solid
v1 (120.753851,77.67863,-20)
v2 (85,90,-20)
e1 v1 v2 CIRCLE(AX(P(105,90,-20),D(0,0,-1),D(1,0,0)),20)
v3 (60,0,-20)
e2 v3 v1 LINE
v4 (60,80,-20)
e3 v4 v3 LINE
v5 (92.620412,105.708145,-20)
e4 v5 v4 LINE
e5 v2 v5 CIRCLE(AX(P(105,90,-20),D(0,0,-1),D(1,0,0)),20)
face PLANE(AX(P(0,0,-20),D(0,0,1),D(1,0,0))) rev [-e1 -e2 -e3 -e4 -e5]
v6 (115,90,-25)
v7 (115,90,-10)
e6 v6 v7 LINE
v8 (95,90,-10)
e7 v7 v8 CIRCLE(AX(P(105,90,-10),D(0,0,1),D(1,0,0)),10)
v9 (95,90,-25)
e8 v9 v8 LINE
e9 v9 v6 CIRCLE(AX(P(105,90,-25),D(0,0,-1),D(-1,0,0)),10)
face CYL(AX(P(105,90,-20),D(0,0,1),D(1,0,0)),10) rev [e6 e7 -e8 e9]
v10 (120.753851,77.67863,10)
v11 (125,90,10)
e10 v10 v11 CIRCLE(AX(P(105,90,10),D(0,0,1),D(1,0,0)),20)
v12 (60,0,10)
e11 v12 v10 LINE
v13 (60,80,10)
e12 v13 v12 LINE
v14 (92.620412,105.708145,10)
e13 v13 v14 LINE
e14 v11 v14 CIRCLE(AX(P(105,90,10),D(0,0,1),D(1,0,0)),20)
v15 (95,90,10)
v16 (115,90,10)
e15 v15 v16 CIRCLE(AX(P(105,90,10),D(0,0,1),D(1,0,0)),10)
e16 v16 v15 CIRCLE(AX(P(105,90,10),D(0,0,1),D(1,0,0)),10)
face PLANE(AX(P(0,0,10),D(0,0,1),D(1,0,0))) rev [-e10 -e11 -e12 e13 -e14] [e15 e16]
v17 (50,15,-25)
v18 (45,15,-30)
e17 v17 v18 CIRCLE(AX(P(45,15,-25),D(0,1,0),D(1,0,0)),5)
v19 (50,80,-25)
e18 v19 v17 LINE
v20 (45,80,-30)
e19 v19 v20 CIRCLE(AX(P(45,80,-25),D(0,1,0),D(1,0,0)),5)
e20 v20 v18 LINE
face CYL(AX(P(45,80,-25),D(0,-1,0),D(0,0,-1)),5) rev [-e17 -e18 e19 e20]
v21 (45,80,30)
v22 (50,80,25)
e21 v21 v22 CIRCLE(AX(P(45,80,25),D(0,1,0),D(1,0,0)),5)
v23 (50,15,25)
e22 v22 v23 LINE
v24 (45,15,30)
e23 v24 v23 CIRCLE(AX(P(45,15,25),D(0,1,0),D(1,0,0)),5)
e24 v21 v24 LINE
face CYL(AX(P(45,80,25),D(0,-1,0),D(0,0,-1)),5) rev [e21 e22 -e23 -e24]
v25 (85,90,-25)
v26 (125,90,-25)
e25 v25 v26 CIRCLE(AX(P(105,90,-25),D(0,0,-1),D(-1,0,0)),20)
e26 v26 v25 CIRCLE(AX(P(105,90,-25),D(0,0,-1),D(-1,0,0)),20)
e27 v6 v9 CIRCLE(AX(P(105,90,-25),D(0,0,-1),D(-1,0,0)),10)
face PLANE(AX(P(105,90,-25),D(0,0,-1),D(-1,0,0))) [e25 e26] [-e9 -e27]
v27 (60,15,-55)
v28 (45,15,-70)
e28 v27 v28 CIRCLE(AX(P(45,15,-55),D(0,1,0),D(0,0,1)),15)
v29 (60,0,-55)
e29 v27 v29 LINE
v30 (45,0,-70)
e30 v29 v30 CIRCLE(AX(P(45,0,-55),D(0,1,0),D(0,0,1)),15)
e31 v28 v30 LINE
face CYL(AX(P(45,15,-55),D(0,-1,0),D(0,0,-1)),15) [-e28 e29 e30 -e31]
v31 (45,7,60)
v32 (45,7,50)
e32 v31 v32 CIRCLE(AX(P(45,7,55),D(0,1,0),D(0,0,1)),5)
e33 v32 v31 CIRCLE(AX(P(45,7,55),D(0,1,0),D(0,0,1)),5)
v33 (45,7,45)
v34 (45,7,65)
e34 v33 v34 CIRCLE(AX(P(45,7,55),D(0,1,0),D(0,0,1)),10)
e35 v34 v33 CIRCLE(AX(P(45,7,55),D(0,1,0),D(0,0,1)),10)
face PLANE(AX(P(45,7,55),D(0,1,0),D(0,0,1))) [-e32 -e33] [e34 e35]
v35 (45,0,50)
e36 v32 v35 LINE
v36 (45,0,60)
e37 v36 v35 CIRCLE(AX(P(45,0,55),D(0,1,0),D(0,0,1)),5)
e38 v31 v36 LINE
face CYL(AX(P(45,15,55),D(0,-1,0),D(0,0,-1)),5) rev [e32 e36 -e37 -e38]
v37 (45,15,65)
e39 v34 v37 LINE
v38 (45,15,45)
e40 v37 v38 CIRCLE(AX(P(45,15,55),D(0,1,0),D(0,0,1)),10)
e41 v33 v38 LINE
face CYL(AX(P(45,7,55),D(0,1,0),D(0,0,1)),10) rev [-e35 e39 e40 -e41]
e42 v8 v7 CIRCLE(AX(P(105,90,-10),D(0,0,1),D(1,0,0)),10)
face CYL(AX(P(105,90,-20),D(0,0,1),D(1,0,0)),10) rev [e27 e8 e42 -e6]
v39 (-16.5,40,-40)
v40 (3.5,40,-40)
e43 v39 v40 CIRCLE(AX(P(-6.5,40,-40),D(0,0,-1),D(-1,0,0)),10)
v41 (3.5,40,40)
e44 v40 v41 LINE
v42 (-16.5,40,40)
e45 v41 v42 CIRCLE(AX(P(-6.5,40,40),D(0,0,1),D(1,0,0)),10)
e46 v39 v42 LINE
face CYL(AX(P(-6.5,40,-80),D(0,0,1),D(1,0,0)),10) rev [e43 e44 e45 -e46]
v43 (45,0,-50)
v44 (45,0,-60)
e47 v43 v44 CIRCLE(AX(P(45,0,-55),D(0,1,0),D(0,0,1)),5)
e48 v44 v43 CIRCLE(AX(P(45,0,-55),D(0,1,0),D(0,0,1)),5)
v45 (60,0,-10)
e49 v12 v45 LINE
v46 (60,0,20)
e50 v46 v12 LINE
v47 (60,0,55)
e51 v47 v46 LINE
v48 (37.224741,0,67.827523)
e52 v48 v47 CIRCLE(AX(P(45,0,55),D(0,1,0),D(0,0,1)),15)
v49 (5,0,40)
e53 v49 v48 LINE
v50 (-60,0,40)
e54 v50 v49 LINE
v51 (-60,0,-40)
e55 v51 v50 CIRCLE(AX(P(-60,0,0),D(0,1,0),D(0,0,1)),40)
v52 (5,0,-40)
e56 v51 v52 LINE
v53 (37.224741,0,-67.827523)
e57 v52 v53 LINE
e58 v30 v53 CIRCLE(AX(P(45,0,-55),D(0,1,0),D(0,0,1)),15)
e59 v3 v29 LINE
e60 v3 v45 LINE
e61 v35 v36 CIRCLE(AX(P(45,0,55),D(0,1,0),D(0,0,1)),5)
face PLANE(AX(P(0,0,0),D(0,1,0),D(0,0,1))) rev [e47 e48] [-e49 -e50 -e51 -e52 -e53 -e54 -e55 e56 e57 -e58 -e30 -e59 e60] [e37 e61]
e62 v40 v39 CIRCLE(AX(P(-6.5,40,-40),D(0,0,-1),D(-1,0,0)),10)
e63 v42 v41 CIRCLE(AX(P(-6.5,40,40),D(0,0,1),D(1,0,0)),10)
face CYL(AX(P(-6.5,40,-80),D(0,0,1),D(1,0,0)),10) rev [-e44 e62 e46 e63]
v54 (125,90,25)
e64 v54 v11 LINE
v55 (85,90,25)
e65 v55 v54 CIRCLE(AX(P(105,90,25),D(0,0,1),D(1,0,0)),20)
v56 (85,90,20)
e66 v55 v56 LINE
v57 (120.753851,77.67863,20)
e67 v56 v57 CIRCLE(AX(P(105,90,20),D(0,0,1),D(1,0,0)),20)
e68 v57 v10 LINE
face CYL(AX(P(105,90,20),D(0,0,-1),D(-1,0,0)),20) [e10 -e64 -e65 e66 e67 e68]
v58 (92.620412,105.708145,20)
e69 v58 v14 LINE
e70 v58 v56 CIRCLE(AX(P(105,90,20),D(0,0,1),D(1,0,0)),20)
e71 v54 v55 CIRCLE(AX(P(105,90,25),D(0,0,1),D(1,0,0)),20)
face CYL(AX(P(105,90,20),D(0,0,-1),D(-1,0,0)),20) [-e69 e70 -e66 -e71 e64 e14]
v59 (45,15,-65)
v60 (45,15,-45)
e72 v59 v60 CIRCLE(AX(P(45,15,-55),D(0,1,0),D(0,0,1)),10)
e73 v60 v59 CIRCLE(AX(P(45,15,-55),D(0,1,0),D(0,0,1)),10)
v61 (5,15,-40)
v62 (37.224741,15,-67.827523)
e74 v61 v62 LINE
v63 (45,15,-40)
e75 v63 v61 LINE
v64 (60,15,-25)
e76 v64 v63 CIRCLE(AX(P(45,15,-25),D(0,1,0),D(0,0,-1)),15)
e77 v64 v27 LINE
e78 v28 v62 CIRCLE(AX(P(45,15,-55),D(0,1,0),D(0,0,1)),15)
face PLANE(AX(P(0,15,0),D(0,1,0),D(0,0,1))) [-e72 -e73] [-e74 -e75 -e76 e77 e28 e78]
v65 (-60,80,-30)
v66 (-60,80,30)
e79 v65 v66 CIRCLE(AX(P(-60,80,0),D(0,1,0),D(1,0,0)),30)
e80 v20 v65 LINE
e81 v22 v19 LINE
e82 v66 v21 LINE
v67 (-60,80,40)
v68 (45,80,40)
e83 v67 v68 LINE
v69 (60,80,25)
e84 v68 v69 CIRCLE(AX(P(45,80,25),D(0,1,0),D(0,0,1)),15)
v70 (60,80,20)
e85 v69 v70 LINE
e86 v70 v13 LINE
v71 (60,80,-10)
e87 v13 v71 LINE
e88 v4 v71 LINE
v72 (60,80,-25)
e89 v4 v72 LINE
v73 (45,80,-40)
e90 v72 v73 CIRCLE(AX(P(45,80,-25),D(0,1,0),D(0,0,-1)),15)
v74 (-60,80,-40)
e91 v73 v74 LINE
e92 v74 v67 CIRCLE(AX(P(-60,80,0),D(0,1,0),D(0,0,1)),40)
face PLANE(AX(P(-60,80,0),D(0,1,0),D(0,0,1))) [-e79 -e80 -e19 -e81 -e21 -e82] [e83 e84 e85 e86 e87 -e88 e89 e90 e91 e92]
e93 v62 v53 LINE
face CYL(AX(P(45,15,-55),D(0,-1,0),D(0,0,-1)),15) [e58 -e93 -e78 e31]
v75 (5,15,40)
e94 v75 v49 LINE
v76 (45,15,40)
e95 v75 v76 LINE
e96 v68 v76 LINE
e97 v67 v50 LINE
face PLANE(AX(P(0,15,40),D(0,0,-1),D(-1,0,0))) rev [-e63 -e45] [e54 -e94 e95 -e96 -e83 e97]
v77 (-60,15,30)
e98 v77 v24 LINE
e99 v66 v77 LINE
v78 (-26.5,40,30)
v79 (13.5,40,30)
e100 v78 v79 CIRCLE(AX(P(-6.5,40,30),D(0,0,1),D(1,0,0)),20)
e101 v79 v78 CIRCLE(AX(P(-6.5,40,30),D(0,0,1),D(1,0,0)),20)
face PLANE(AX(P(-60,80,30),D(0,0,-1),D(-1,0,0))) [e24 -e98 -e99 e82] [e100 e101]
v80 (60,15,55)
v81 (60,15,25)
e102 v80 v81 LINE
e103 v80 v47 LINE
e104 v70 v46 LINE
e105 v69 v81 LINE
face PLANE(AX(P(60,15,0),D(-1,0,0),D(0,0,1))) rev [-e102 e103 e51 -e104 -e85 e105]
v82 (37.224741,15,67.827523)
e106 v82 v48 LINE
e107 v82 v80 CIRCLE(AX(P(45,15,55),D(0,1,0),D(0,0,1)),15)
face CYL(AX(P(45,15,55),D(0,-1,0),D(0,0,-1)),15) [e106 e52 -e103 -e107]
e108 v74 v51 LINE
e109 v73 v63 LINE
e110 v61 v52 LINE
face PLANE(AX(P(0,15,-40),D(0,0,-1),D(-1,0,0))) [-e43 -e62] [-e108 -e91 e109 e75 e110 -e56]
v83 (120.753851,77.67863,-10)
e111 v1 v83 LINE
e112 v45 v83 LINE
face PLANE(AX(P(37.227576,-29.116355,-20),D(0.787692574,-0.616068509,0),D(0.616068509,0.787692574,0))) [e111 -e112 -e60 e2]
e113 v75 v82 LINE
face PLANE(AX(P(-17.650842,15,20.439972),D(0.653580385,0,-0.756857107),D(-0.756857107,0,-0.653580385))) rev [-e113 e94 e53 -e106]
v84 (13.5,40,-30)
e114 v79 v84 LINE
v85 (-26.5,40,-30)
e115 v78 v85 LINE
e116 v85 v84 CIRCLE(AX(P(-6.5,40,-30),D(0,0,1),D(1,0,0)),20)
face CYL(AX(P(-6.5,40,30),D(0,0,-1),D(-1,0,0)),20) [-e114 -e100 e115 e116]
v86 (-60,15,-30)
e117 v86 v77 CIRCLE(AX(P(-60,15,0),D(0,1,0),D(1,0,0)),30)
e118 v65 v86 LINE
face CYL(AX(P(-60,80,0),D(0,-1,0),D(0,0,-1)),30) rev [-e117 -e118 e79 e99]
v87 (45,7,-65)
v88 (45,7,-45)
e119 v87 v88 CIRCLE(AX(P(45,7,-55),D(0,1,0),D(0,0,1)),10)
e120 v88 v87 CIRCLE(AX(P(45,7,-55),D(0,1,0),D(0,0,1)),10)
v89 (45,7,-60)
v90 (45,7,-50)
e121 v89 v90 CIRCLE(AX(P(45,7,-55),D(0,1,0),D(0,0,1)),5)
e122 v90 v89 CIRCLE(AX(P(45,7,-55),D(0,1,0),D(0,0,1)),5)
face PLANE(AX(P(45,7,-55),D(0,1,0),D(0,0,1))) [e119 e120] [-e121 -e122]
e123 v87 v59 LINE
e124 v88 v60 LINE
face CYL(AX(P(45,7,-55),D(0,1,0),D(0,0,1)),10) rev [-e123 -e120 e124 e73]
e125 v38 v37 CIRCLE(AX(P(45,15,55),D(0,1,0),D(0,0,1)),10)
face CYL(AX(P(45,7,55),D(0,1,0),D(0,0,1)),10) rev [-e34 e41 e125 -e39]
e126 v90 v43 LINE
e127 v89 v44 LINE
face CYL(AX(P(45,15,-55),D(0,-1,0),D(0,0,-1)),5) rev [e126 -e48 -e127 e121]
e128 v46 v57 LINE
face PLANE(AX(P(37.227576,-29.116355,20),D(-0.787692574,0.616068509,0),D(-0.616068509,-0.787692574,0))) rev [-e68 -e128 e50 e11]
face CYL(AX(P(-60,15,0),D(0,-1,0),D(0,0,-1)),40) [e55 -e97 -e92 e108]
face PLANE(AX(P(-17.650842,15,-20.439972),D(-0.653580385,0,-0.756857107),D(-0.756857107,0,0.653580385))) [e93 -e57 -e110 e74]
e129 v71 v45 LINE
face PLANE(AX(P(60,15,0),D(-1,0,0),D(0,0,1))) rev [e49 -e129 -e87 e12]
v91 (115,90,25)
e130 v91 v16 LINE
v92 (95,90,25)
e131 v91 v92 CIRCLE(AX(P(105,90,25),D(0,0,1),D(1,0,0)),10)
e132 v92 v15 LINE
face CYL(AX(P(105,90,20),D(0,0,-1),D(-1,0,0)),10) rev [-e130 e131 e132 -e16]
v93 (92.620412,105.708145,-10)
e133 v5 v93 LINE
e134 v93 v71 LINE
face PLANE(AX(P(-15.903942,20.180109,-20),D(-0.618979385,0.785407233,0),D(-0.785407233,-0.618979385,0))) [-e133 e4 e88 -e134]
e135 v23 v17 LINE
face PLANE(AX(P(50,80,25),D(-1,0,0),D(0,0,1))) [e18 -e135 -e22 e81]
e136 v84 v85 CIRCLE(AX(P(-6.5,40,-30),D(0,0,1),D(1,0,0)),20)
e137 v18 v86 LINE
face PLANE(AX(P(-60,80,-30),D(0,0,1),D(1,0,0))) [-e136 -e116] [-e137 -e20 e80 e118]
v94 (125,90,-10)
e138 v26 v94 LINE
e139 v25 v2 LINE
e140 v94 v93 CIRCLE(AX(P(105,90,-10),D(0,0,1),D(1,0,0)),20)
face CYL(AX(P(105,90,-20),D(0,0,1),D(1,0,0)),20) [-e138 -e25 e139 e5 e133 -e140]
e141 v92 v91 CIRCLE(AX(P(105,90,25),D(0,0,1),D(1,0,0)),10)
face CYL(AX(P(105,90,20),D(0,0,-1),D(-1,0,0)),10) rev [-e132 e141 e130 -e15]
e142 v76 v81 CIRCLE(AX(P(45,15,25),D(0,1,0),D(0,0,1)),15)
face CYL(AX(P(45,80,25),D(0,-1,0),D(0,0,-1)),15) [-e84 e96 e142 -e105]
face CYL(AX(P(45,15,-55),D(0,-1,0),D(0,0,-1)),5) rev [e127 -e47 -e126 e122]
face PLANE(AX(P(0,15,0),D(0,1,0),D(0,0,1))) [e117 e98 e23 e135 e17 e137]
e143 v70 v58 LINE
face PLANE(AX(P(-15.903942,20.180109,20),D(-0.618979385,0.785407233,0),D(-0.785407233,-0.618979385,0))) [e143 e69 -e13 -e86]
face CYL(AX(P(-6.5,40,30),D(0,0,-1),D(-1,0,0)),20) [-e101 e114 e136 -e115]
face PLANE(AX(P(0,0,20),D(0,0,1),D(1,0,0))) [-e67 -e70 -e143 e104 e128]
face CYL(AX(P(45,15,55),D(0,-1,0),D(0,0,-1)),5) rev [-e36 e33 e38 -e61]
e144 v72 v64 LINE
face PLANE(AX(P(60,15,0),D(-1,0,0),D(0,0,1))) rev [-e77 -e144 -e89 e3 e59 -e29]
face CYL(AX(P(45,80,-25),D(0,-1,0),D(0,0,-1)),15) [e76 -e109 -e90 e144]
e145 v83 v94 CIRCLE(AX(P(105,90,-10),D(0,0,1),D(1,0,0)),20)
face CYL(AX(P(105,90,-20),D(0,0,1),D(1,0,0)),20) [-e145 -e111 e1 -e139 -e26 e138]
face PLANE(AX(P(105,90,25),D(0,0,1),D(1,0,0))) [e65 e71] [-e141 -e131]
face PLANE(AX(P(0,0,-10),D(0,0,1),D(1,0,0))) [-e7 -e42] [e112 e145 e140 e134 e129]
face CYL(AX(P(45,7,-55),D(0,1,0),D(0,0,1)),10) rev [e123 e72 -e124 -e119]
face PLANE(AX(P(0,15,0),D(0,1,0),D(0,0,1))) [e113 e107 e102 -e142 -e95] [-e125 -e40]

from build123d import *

# Parameters (mm, degrees)
BASE_PLATE_SKETCH_R       = 5
BASE_PLATE_DEPTH          = 15
HOUSING_WALL_DEPTH        = 65
EAR_RECESSES_SKETCH_R     = 10
EAR_RECESSES_2X_20_DEPTH  = 8
CROSS_BORE_SKETCH_R       = 10
CROSS_BORE_DEPTH          = 120
CROSS_START               = 60
CROSS_PIN_SKETCH_R        = 20
CROSS_PIN_SKETCH_R_2      = 10
CROSS_PIN_DEPTH           = 60
LUG_1_SKETCH_R            = 20
LUG_1_SKETCH_R_2          = 10
LUG_1_DEPTH               = 10
LUG_1_PIN_BOSS_SKETCH_R   = 20
LUG_1_PIN_BOSS_SKETCH_R_2 = 10
LUG_1_PIN_BOSS_DEPTH      = 5
LUG_START                 = -10
LUG_2_SKETCH_R            = 20
LUG_2_SKETCH_R_2          = 10
LUG_2_DEPTH               = 10
LUG_START_2               = 5
LUG_2_PIN_BOSS_SKETCH_R   = 20
LUG_2_PIN_BOSS_SKETCH_R_2 = 10
LUG_2_PIN_BOSS_DEPTH      = 5


with BuildPart() as part:
    # Base Plate Sketch → Base Plate (new body)
    # profile 1 of 3: a face of its own
    with BuildSketch(Plane(origin=(0, 0, 0), x_dir=(1, 0, 0), z_dir=(0, 1, 0))):
        with BuildLine():
            Line((-60, -40), (45, -40))
            ThreePointArc((45, -40), (55.606601718, -35.606601718), (60, -25))
            Line((60, -25), (60, 25))
            ThreePointArc((60, 25), (55.606601718, 35.606601718), (45, 40))
            Line((45, 40), (-60, 40))
            ThreePointArc((-60, 40), (-100, 0), (-60, -40))
        make_face()
    # profile 2 of 3: a face of its own
    with BuildSketch(Plane(origin=(0, 0, 0), x_dir=(1, 0, 0), z_dir=(0, 1, 0))):
        with BuildLine():
            Line((60, -40), (60, -25))
            ThreePointArc((60, -25), (55.606601718, -35.606601718), (45, -40))
            Line((45, -40), (5, -40))
            Line((5, -40), (33.441882385, -64.560853371))
            Line((33.441882385, -64.560853371), (37.224740847, -67.827522953))
            ThreePointArc((37.224740847, -67.827522953), (52.361083912, -68.06959998), (60, -55))
            Line((60, -55), (60, -40))
        make_face()
        with Locations(Location((45, -55, 0), (0, 0, 270))):
            Circle(BASE_PLATE_SKETCH_R, mode=Mode.SUBTRACT)
    # profile 3 of 3: a face of its own
    with BuildSketch(Plane(origin=(0, 0, 0), x_dir=(1, 0, 0), z_dir=(0, 1, 0))):
        with BuildLine():
            Line((60, 40), (60, 55))
            ThreePointArc((60, 55), (52.361083912, 68.06959998), (37.224740847, 67.827522953))
            Line((37.224740847, 67.827522953), (33.441882385, 64.560853371))
            Line((33.441882385, 64.560853371), (5, 40))
            Line((5, 40), (45, 40))
            ThreePointArc((45, 40), (55.606601718, 35.606601718), (60, 25))
            Line((60, 25), (60, 40))
        make_face()
        with Locations(Location((45, 55, 0), (0, 0, 270))):
            Circle(BASE_PLATE_SKETCH_R, mode=Mode.SUBTRACT)
    extrude(amount=BASE_PLATE_DEPTH)

    # Housing Wall Sketch → Housing Wall (add)
    with BuildSketch(Plane(origin=(0, 15, 0), x_dir=(1, 0, 0), z_dir=(0, 1, 0))):
        with BuildLine():
            Line((45, 40), (-60, 40))
            ThreePointArc((-60, 40), (-100, 0), (-60, -40))
            Line((-60, -40), (45, -40))
            ThreePointArc((45, -40), (55.606601718, -35.606601718), (60, -25))
            Line((60, -25), (60, 25))
            ThreePointArc((60, 25), (55.606601718, 35.606601718), (45, 40))
        make_face()
        with BuildLine():
            Line((45, 30), (-60, 30))
            ThreePointArc((-60, 30), (-90, 0), (-60, -30))
            Line((-60, -30), (45, -30))
            ThreePointArc((45, -30), (48.535533906, -28.535533906), (50, -25))
            Line((50, -25), (50, 25))
            ThreePointArc((50, 25), (48.535533906, 28.535533906), (45, 30))
        make_face(mode=Mode.SUBTRACT)
    extrude(amount=HOUSING_WALL_DEPTH)

    # Ear Recesses Sketch → Ear Recesses 2xØ20 (cut)
    with BuildSketch(Plane(origin=(0, 15, 0), x_dir=(1, 0, 0), z_dir=(0, 1, 0))):
        with Locations(Location((45, -55, 0), (0, 0, 270))):
            Circle(EAR_RECESSES_SKETCH_R)
        with Locations(Location((45, 55, 0), (0, 0, 270))):
            Circle(EAR_RECESSES_SKETCH_R)
    extrude(amount=-EAR_RECESSES_2X_20_DEPTH, mode=Mode.SUBTRACT)

    # Cross Bore Sketch → Cross Bore (cut)
    with BuildSketch(Plane.XY.offset(40)):
        with Locations((-6.5, 40)):
            Circle(CROSS_BORE_SKETCH_R)
    extrude(amount=-CROSS_BORE_DEPTH, mode=Mode.SUBTRACT)

    # Cross Pin Sketch → Cross Pin (add)
    with BuildSketch(Plane.XY.offset(-30).offset(CROSS_START)):
        with Locations((-6.5, 40)):
            Circle(CROSS_PIN_SKETCH_R)
        with Locations((-6.5, 40)):
            Circle(CROSS_PIN_SKETCH_R_2, mode=Mode.SUBTRACT)
    extrude(amount=-CROSS_PIN_DEPTH)

    # Lug 1 Sketch → Lug 1 (add)
    # profile 1 of 2: a face of its own
    with BuildSketch(Plane.XY.offset(10)):
        with BuildLine():
            Line((92.6204123, 105.708144651), (60, 80))
            Line((60, 80), (60, 0))
            Line((60, 0), (120.753851487, 77.678629812))
            ThreePointArc((120.753851487, 77.678629812), (90.884057256, 75.831719919), (92.6204123, 105.708144651))
        make_face()
    # profile 2 of 2: a face of its own
    with BuildSketch(Plane.XY.offset(10)):
        with Locations((105, 90)):
            Circle(LUG_1_SKETCH_R)
        with Locations((105, 90)):
            Circle(LUG_1_SKETCH_R_2, mode=Mode.SUBTRACT)
    extrude(amount=LUG_1_DEPTH)

    # Lug 1 Pin Boss Sketch → Lug 1 Pin Boss (add)
    with BuildSketch(Plane.XY.offset(20)):
        with Locations(Location((105, 90, 0), (0, 0, 128.241642007))):
            Circle(LUG_1_PIN_BOSS_SKETCH_R)
        with Locations((105, 90)):
            Circle(LUG_1_PIN_BOSS_SKETCH_R_2, mode=Mode.SUBTRACT)
    extrude(amount=LUG_1_PIN_BOSS_DEPTH)

    # Lug 2 Sketch → Lug 2 (add)
    # profile 1 of 2: a face of its own
    with BuildSketch(Plane.XY.offset(-10).offset(LUG_START)):
        with BuildLine():
            ThreePointArc((120.753851487, 77.678629812), (90.884057256, 75.831719919), (92.6204123, 105.708144651))
            Line((92.6204123, 105.708144651), (60, 80))
            Line((60, 80), (60, 0))
            Line((60, 0), (120.753851487, 77.678629812))
        make_face()
    # profile 2 of 2: a face of its own
    with BuildSketch(Plane.XY.offset(-10).offset(LUG_START)):
        with Locations(Location((105, 90, 0), (0, 0, 128.241642007))):
            Circle(LUG_2_SKETCH_R)
        with Locations((105, 90)):
            Circle(LUG_2_SKETCH_R_2, mode=Mode.SUBTRACT)
    extrude(amount=LUG_2_DEPTH)

    # Lug 2 Pin Boss Sketch → Lug 2 Pin Boss (add)
    with BuildSketch(Plane(origin=(0, 0, -20), x_dir=(-1, 0, 0), z_dir=(0, 0, -1)).offset(LUG_START_2)):
        with Locations(Location((-105, 90, 0), (0, 0, 51.758357993))):
            Circle(LUG_2_PIN_BOSS_SKETCH_R)
        with Locations(Location((-105, 90, 0), (0, 0, 180))):
            Circle(LUG_2_PIN_BOSS_SKETCH_R_2, mode=Mode.SUBTRACT)
    extrude(amount=-LUG_2_PIN_BOSS_DEPTH)


solid = part.part
